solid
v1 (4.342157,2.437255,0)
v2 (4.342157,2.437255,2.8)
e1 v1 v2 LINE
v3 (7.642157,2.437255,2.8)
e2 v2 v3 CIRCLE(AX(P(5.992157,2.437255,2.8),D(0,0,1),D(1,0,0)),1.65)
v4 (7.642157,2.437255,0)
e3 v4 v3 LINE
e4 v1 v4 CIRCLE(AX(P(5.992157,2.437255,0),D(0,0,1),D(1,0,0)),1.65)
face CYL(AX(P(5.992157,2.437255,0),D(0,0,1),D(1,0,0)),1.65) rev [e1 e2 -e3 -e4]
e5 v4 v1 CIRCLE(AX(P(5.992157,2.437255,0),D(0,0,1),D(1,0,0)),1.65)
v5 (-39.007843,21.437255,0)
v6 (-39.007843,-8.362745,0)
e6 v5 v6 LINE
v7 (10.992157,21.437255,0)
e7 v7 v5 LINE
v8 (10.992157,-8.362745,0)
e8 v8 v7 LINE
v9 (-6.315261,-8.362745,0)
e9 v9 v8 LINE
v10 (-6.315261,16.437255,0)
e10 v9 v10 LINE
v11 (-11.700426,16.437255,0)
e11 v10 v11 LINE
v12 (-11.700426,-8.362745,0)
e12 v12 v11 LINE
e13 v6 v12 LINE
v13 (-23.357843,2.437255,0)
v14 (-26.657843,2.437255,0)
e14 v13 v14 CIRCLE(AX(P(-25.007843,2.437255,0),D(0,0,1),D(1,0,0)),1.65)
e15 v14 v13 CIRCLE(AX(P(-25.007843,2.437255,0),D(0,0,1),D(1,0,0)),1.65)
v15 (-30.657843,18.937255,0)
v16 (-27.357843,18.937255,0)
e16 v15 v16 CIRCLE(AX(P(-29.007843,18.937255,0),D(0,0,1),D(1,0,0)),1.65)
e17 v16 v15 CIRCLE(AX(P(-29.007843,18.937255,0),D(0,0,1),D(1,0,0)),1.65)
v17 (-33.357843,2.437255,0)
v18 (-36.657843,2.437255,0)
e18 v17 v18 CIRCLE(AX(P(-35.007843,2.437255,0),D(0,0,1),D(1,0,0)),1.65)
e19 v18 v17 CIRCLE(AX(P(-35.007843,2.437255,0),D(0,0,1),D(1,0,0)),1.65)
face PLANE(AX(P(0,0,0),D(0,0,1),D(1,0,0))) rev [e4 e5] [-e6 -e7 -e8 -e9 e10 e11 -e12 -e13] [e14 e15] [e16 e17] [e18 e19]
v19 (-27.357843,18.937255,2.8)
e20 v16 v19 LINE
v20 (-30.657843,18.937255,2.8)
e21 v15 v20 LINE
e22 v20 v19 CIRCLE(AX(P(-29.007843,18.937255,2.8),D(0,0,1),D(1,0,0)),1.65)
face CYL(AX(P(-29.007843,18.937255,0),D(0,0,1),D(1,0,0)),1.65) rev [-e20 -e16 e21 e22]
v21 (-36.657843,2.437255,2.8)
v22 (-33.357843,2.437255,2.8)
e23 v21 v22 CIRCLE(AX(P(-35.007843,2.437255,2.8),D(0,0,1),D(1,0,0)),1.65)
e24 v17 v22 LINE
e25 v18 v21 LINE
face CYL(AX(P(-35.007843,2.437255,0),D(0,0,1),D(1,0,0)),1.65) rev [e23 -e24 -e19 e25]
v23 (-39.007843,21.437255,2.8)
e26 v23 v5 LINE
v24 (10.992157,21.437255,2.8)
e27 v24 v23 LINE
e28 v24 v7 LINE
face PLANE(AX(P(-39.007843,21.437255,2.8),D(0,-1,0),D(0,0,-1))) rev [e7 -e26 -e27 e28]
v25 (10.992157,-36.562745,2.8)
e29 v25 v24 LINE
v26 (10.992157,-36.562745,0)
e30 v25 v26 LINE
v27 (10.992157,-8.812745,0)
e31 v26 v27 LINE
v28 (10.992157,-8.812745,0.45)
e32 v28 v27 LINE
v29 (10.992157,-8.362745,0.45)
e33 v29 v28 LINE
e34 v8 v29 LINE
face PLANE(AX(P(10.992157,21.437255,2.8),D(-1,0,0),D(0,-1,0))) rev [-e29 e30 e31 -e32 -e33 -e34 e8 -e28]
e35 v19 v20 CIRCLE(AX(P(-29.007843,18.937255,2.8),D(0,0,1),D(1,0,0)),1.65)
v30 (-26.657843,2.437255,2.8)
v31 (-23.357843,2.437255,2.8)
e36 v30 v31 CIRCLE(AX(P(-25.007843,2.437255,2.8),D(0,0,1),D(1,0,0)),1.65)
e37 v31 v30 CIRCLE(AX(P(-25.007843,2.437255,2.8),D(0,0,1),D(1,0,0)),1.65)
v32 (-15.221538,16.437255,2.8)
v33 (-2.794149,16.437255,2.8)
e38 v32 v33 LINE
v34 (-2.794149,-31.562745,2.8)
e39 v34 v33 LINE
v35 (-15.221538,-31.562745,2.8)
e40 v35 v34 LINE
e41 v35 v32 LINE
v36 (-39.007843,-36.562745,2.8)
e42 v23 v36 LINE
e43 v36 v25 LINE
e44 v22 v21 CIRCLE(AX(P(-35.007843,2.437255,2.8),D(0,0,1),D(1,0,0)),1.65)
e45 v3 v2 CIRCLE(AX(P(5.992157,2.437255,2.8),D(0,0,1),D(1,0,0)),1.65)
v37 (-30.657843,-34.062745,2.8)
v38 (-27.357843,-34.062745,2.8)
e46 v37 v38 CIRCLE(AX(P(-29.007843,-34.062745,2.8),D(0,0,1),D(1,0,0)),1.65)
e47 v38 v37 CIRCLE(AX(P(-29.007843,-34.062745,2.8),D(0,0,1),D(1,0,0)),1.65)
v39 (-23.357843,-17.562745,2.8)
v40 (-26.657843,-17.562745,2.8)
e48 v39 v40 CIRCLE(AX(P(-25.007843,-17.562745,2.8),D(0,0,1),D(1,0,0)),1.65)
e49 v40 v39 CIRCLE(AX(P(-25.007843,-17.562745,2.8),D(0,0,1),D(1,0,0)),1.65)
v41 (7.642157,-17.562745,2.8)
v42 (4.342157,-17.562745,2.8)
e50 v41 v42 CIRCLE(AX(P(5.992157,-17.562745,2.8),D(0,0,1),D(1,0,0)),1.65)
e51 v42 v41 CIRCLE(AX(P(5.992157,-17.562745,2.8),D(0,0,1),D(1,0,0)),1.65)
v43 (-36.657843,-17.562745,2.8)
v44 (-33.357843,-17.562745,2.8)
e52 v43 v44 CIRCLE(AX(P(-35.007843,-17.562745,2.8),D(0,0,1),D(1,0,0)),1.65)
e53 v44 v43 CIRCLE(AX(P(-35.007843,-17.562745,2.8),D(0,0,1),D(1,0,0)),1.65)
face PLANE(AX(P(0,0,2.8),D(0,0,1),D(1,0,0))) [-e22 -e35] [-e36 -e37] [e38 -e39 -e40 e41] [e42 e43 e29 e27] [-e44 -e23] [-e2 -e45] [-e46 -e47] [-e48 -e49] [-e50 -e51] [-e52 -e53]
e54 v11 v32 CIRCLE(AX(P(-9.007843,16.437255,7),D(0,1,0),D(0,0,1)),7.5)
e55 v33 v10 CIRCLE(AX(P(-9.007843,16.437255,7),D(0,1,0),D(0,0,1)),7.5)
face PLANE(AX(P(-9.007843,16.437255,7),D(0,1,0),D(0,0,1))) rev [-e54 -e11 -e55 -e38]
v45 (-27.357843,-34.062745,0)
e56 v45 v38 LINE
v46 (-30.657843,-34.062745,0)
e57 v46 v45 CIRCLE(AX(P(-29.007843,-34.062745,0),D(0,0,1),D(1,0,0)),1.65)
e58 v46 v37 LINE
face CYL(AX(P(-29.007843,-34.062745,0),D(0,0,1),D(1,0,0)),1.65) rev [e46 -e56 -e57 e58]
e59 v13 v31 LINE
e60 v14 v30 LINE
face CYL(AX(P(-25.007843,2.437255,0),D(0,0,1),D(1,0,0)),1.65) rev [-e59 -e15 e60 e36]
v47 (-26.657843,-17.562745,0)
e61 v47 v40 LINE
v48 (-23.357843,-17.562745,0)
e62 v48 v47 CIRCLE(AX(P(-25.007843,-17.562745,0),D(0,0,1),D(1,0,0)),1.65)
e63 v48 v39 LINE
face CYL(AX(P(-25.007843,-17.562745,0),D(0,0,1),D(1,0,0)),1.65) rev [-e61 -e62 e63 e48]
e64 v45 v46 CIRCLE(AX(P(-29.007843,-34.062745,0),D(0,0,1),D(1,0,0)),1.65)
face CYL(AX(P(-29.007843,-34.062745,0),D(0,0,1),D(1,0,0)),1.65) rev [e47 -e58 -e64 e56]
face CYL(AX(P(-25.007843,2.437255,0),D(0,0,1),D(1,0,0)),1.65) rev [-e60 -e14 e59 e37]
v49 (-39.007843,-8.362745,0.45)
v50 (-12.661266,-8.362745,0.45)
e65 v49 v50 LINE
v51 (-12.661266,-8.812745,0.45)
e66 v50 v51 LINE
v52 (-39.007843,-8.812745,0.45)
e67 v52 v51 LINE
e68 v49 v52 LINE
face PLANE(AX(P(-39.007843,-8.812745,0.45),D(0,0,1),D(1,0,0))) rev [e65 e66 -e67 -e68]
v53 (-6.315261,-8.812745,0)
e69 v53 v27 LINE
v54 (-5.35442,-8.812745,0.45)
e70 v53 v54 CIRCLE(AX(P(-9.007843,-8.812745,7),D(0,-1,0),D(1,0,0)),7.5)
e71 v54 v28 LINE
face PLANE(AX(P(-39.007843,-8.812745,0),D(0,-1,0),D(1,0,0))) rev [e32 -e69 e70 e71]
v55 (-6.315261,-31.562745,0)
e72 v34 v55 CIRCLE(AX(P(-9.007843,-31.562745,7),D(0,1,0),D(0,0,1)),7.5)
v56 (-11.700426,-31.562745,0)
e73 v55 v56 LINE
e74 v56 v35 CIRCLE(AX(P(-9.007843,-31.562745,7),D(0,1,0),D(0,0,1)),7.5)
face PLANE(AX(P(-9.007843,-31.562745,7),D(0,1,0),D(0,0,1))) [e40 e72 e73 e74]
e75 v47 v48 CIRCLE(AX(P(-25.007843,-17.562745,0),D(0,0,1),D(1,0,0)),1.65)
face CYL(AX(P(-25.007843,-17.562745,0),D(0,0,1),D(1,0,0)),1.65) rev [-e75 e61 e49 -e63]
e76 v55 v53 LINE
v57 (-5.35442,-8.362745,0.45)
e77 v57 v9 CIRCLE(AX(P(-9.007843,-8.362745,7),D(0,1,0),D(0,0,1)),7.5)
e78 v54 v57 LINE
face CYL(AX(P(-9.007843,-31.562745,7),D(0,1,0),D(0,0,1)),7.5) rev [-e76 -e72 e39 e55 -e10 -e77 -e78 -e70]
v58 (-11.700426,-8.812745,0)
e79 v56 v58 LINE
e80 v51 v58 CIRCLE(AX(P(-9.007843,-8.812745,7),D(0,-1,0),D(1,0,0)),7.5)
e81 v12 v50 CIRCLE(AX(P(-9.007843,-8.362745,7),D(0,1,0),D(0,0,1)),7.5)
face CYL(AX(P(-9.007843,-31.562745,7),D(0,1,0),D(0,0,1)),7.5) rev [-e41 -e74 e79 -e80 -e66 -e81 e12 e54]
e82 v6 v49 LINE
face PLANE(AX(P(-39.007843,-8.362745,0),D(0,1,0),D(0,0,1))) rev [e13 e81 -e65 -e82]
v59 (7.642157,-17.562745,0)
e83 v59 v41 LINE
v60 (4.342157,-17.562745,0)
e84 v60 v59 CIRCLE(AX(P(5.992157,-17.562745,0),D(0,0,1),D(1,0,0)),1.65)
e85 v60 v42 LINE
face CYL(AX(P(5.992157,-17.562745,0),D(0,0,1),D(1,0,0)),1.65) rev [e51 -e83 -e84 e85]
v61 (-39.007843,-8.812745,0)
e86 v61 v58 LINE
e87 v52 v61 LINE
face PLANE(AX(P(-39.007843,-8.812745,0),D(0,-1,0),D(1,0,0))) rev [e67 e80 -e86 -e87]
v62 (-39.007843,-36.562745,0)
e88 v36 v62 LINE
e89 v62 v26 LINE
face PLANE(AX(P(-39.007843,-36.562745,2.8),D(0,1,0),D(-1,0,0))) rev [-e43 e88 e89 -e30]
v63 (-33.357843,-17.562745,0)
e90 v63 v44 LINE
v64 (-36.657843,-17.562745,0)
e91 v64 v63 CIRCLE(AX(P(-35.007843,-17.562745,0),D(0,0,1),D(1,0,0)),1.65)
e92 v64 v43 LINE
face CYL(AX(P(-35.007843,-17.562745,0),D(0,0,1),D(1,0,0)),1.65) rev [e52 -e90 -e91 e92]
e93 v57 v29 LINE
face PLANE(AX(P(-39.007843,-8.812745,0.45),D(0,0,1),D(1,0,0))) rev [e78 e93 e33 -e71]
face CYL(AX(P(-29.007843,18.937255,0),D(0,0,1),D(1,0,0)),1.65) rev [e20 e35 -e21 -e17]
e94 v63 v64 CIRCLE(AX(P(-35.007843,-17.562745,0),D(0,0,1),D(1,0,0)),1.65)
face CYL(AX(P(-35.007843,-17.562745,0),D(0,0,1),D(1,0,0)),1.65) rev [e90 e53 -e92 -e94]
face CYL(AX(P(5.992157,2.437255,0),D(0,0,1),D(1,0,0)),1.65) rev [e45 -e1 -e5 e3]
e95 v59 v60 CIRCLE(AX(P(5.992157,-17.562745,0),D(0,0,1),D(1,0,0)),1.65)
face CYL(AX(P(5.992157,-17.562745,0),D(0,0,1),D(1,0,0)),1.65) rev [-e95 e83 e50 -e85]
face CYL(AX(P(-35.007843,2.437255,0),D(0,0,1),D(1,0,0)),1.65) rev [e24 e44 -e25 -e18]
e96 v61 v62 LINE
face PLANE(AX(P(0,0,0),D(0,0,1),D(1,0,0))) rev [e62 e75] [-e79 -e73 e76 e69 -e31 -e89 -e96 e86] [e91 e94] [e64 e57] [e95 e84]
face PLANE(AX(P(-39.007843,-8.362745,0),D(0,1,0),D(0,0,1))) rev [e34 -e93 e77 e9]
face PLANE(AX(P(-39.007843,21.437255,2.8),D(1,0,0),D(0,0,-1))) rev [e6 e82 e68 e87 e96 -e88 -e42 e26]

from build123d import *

# Parameters (mm, degrees)
SKETCH_1_W          = 50
SKETCH_1_H          = 58
EXTRUDE_1_DEPTH     = 2.8
SKETCH_2_R          = 1.65
CUT_EXTRUDE_1_DEPTH = 54.537707789
SKETCH_3_W          = 0.45
SKETCH_3_H          = 0.45
CUT_EXTRUDE_2_DEPTH = 63.005437899
CUT_EXTRUDE_3_DEPTH = 48


with BuildPart() as part:
    # 草图1 → 凸台-拉伸1 (new body)
    with BuildSketch(Plane.XY):
        with Locations((-14.007843137, -7.562745098)):
            Rectangle(SKETCH_1_W, SKETCH_1_H)
    extrude(amount=EXTRUDE_1_DEPTH)

    # 草图2 → 切除-拉伸1 (cut, through all)
    with BuildSketch(Plane.XY.offset(2.8)):
        with Locations((-29.007843137, 18.937254902)):
            Circle(SKETCH_2_R)
        with Locations((-35.007843137, 2.437254902)):
            Circle(SKETCH_2_R)
        with Locations((-25.007843137, 2.437254902)):
            Circle(SKETCH_2_R)
        with Locations((5.992156863, 2.437254902)):
            Circle(SKETCH_2_R)
        with Locations((-35.007843137, -17.562745098)):
            Circle(SKETCH_2_R)
        with Locations((-25.007843137, -17.562745098)):
            Circle(SKETCH_2_R)
        with Locations((-29.007843137, -34.062745098)):
            Circle(SKETCH_2_R)
        with Locations((5.992156863, -17.562745098)):
            Circle(SKETCH_2_R)
    extrude(amount=-CUT_EXTRUDE_1_DEPTH, mode=Mode.SUBTRACT)

    # 草图3 → 切除-拉伸2 (cut, through all)
    with BuildSketch(Plane(origin=(10.992156863, 0, 0), x_dir=(0, 0, -1), z_dir=(1, 0, 0))):
        with Locations((-0.225, -8.587745098)):
            Rectangle(SKETCH_3_W, SKETCH_3_H)
    extrude(amount=-CUT_EXTRUDE_2_DEPTH, mode=Mode.SUBTRACT)

    # 草图5 → 切除-拉伸3 (cut)
    with BuildSketch(Plane(origin=(0, 16.437254902, 0), x_dir=(1, 0, 0), z_dir=(0, 1, 0))):
        with BuildLine():
            Line((-2.794148584, -2.8), (-15.22153769, -2.8))
            ThreePointArc((-15.22153769, -2.8), (-13.675866521, -1.129773625), (-11.700425541, 0))
            Line((-11.700425541, 0), (-6.408228111, 0.035055203))
            ThreePointArc((-6.408228111, 0.035055203), (-4.378805339, -1.098982371), (-2.794148584, -2.8))
        make_face()
    extrude(amount=-CUT_EXTRUDE_3_DEPTH, mode=Mode.SUBTRACT)


solid = part.part
